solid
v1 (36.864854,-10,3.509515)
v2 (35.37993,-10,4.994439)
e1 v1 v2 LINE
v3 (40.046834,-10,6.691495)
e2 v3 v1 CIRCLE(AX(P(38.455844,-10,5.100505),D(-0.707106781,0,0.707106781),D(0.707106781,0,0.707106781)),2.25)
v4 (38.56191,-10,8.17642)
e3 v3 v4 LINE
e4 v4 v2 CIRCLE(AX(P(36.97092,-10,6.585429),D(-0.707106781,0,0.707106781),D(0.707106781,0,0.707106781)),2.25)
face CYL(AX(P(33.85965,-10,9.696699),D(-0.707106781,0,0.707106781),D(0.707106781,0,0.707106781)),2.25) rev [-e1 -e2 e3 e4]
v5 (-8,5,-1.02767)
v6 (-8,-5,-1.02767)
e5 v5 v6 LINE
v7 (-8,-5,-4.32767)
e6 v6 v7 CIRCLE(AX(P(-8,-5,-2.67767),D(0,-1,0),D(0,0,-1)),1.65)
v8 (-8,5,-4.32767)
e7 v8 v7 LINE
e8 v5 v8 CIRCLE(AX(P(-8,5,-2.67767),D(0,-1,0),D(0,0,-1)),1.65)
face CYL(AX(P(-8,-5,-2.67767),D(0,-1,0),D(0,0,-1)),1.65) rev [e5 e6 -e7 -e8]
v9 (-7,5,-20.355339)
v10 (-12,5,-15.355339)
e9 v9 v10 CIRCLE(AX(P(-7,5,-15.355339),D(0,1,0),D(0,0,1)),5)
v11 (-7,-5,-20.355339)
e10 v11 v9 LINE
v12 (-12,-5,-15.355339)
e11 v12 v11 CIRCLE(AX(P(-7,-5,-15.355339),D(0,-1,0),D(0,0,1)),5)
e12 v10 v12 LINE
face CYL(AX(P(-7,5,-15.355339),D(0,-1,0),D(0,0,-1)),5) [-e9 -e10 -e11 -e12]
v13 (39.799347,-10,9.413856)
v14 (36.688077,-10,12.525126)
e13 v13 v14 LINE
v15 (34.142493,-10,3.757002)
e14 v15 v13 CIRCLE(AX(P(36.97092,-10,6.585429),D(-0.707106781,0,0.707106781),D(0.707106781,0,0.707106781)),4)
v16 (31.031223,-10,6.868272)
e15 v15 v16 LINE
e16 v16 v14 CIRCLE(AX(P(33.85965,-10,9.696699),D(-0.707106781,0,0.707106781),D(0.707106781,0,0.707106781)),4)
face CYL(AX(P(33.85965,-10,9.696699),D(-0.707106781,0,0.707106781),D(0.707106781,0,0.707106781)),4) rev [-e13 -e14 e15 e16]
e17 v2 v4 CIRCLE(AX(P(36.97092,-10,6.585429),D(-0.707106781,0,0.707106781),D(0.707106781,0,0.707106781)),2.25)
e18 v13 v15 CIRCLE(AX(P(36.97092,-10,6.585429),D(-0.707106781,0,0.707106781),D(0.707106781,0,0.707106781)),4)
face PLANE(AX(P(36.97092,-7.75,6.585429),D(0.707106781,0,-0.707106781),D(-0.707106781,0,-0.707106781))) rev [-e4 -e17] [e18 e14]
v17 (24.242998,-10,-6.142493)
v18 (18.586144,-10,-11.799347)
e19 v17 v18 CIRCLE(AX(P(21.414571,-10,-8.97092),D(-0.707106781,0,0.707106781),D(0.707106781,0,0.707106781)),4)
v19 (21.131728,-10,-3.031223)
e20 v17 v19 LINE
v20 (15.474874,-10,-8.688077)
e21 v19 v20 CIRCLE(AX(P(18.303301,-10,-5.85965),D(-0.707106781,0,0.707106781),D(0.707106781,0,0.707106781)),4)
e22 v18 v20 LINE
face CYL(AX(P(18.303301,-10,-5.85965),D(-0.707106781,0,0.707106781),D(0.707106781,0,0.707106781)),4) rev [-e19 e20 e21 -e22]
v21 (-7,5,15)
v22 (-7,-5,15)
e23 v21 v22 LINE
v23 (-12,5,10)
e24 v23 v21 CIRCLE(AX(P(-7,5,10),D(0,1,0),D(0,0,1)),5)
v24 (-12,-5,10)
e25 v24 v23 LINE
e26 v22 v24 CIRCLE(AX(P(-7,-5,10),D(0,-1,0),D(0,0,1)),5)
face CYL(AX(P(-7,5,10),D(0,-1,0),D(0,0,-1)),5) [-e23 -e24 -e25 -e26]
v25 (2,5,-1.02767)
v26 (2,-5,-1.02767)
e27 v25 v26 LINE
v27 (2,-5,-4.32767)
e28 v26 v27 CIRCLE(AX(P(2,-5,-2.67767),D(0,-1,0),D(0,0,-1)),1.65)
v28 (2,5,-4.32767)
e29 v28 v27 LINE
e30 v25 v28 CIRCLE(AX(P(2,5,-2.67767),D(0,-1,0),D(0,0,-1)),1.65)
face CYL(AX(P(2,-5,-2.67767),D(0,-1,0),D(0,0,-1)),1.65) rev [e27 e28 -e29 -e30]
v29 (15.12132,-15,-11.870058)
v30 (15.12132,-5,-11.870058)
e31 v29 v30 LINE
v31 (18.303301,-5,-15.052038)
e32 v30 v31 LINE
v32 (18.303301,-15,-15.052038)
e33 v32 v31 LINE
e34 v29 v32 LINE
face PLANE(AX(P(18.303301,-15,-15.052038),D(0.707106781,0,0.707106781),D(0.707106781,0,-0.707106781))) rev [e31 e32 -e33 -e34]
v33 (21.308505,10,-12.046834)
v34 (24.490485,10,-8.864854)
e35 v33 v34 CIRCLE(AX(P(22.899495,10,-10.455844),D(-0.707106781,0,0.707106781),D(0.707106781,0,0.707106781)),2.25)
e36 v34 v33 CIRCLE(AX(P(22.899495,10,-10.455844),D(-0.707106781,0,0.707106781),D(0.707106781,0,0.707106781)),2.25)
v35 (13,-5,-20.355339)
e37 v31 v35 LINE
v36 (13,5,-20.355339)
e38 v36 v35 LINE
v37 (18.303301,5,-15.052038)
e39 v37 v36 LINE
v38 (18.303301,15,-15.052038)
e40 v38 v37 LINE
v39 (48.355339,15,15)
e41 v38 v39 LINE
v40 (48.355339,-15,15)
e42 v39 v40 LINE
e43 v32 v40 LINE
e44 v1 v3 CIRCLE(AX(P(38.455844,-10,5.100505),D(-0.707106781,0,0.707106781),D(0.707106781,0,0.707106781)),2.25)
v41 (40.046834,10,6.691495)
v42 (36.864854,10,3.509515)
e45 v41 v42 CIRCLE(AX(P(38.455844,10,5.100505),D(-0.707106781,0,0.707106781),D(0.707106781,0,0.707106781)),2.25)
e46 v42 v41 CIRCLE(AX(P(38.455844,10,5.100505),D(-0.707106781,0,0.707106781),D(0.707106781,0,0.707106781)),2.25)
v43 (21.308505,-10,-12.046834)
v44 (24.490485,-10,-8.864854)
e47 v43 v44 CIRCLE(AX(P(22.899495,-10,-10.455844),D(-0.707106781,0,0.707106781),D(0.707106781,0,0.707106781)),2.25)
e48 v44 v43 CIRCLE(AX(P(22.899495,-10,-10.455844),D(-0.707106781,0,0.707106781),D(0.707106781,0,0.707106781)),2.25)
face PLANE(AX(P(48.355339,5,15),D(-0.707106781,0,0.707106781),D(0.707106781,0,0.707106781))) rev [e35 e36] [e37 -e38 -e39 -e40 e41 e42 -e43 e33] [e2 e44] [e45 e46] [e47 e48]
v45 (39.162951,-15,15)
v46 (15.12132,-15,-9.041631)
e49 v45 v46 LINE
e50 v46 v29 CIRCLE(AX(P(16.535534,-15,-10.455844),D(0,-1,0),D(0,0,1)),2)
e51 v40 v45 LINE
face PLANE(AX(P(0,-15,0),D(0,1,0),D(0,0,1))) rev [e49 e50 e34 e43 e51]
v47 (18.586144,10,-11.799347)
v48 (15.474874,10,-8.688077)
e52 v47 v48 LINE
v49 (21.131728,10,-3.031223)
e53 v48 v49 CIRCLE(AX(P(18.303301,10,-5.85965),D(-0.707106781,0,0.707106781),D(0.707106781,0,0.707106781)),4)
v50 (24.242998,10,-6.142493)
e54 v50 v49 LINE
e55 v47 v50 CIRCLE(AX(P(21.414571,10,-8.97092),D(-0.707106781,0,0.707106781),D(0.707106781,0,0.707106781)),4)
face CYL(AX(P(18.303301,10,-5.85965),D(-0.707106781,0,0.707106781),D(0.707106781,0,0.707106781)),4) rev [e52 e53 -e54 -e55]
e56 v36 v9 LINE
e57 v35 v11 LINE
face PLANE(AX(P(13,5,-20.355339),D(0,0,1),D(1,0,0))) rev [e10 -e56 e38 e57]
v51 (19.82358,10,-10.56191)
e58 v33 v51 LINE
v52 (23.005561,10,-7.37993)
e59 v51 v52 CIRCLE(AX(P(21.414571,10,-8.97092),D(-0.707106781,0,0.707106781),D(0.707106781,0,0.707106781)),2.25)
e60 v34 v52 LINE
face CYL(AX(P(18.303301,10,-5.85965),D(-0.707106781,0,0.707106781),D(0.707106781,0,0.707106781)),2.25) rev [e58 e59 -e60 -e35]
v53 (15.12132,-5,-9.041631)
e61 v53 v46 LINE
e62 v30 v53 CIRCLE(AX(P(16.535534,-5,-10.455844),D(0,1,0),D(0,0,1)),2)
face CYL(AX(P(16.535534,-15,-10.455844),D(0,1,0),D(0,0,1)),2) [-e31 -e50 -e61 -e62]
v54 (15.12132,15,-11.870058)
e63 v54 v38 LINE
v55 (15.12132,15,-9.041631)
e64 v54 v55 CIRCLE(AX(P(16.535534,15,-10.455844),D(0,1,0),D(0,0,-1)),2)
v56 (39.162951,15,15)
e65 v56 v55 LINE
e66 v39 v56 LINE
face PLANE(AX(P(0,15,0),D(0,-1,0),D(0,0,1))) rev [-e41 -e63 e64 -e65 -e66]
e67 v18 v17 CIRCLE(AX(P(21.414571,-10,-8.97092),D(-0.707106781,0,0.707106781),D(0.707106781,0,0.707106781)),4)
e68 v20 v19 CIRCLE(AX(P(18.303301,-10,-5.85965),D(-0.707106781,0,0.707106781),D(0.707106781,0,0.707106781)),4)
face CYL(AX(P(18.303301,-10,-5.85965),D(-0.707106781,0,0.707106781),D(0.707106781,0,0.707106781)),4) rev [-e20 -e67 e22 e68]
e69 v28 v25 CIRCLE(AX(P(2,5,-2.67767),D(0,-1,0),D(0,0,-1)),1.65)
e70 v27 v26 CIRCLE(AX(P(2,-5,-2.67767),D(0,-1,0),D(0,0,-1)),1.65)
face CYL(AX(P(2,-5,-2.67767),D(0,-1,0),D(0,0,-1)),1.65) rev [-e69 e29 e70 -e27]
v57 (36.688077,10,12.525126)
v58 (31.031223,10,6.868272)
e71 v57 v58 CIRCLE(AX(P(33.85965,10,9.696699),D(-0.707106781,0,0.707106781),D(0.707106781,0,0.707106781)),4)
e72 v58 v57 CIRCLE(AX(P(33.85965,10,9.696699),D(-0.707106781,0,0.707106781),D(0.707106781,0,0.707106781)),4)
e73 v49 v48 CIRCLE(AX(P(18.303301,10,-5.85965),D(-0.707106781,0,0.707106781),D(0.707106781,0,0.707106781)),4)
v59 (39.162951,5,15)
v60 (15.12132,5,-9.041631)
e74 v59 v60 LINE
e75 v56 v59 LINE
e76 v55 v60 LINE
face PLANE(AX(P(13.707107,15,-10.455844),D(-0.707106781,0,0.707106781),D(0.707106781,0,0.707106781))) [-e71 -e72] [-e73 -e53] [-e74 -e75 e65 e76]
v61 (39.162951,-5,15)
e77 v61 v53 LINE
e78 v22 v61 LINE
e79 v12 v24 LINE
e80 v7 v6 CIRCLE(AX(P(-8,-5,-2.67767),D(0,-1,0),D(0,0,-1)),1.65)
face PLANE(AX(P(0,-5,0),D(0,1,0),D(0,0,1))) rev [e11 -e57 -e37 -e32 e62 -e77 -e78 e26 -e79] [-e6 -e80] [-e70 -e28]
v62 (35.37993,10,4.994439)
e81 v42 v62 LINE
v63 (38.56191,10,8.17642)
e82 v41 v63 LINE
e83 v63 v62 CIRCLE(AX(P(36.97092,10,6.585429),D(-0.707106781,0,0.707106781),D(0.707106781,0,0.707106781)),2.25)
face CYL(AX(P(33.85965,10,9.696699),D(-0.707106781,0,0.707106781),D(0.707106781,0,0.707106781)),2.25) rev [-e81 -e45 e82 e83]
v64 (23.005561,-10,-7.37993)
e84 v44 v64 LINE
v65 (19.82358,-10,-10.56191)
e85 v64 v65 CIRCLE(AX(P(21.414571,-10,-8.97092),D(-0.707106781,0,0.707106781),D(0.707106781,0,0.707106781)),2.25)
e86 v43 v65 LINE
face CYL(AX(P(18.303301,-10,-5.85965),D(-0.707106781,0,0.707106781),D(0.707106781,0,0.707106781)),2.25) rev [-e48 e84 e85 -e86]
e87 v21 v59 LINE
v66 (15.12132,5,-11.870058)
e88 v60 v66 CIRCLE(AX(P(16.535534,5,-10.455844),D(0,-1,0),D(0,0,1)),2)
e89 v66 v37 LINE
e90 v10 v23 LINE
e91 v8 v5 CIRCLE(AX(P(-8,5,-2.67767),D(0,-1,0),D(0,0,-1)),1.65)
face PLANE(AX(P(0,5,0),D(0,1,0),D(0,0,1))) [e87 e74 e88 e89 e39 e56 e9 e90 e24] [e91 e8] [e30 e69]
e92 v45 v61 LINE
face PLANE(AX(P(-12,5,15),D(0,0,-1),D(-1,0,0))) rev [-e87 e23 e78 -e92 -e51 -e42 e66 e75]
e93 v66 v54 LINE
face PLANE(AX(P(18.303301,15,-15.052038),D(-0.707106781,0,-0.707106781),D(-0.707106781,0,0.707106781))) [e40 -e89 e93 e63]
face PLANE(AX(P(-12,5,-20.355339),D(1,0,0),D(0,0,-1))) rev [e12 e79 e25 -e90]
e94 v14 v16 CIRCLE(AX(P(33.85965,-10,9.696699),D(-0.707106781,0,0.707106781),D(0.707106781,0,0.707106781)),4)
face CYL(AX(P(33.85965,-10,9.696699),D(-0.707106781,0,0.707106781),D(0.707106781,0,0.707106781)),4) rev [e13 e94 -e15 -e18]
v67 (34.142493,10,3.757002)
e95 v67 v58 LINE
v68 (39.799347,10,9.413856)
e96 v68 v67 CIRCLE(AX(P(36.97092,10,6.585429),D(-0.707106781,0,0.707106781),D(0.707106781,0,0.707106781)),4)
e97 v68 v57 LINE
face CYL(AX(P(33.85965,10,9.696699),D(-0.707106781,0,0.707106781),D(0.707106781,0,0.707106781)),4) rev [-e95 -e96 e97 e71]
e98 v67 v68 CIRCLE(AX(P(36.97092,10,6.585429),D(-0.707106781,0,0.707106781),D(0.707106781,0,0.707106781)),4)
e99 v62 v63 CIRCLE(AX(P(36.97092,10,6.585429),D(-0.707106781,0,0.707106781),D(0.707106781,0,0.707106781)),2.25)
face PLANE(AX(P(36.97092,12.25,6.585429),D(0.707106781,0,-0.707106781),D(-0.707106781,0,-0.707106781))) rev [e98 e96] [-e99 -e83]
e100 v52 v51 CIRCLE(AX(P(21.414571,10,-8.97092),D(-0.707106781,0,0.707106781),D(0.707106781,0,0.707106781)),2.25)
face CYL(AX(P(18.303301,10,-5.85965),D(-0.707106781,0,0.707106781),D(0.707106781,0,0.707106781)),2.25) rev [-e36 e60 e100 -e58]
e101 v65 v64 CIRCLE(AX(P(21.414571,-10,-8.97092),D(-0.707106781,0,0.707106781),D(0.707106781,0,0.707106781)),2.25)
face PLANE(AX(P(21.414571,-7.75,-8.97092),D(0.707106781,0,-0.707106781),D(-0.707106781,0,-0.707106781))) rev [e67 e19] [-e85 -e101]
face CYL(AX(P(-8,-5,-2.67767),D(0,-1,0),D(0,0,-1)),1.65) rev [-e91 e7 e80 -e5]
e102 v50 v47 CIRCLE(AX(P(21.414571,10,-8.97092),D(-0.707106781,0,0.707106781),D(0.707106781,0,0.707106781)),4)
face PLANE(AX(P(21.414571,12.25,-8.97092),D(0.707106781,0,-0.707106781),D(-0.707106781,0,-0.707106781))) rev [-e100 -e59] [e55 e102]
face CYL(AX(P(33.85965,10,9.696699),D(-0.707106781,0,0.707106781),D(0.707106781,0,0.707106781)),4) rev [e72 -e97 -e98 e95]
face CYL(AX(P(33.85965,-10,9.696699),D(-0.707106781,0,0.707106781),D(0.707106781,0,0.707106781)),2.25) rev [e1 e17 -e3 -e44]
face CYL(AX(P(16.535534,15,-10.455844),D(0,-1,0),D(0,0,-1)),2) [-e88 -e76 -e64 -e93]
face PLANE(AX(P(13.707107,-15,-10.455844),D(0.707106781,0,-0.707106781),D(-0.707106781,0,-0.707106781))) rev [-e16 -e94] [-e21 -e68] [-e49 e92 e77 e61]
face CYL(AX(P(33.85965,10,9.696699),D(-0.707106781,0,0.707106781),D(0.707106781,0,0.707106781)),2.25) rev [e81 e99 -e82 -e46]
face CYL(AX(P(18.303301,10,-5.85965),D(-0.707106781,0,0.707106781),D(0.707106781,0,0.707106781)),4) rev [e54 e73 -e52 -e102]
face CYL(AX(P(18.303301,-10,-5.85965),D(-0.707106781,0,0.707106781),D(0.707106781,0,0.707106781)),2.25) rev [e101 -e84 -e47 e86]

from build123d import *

# Parameters (mm, degrees)
EXTRUDE_1_DEPTH                = 5
HOLE_WIZARD_M4_1_D             = 3.3
EXTRUDE_3_DEPTH                = 10
HOLE_WIZARD_M4_1_2_D           = 4.5
HOLE_WIZARD_M4_1_2_CBORE_D     = 8
HOLE_WIZARD_M4_1_2_CBORE_DEPTH = 4.4
FILLET_1_R                     = 2
FILLET_2_R                     = 5


with BuildPart() as part:
    # 草图1 → 凸台-拉伸1 (new, symmetric)
    with BuildSketch(Plane(origin=(0, 0, 0), x_dir=(1, 0, 0), z_dir=(0, 1, 0))):
        Polygon((-12, -15), (48.355339059, -15), (13, 20.355339059), (-12, 20.355339059), align=None)
    extrude(amount=EXTRUDE_1_DEPTH, both=True)

    # Hole Wizard M4 _1 (through all)
    with Locations(Plane(origin=(0, -5, 0), x_dir=(-1, 0, 0), z_dir=(0, -1, 0))):
        with Locations((8, 2.67766953), (-2, 2.67766953)):
            Hole(HOLE_WIZARD_M4_1_D / 2)

    # 草图5 → 凸台-拉伸3 (add)
    with BuildSketch(Plane.XZ.offset(5)):
        Polygon((13.707106781, -10.455844123), (39.162950904, 15), (48.355339059, 15), (18.303300859, -15.0520382), align=None)
    extrude_3 = extrude(amount=EXTRUDE_3_DEPTH)

    # 镜向1: 凸台-拉伸3 across plane
    add(extrude_3.mirror(Plane.ZX))

    # Hole Wizard M4 _1 2 (through all)
    with Locations(Plane(origin=(12.081475452, 0, -12.081475452), x_dir=(0.7071067811865515, 0, 0.7071067811865436), z_dir=(-0.7071067811865436, 0, 0.7071067811865515))):
        with Locations((8.798989873, 10), (30.798989873, 10), (8.798989873, -10), (30.798989873, -10)):
            CounterBoreHole(HOLE_WIZARD_M4_1_2_D / 2, HOLE_WIZARD_M4_1_2_CBORE_D / 2, HOLE_WIZARD_M4_1_2_CBORE_DEPTH)

    # 圆角1
    fillet_1_edges = [part.edges().sort_by_distance(p)[0] for p in [
        (13.707106781, -10, -10.455844123),
        (13.707106781, 10, -10.455844123),
    ]]
    fillet(fillet_1_edges, radius=FILLET_1_R)

    # 圆角2
    fillet_2_edges = [part.edges().sort_by_distance(p)[0] for p in [
        (-12, 0, 15),
        (-12, 0, -20.355339059),
    ]]
    fillet(fillet_2_edges, radius=FILLET_2_R)


solid = part.part
